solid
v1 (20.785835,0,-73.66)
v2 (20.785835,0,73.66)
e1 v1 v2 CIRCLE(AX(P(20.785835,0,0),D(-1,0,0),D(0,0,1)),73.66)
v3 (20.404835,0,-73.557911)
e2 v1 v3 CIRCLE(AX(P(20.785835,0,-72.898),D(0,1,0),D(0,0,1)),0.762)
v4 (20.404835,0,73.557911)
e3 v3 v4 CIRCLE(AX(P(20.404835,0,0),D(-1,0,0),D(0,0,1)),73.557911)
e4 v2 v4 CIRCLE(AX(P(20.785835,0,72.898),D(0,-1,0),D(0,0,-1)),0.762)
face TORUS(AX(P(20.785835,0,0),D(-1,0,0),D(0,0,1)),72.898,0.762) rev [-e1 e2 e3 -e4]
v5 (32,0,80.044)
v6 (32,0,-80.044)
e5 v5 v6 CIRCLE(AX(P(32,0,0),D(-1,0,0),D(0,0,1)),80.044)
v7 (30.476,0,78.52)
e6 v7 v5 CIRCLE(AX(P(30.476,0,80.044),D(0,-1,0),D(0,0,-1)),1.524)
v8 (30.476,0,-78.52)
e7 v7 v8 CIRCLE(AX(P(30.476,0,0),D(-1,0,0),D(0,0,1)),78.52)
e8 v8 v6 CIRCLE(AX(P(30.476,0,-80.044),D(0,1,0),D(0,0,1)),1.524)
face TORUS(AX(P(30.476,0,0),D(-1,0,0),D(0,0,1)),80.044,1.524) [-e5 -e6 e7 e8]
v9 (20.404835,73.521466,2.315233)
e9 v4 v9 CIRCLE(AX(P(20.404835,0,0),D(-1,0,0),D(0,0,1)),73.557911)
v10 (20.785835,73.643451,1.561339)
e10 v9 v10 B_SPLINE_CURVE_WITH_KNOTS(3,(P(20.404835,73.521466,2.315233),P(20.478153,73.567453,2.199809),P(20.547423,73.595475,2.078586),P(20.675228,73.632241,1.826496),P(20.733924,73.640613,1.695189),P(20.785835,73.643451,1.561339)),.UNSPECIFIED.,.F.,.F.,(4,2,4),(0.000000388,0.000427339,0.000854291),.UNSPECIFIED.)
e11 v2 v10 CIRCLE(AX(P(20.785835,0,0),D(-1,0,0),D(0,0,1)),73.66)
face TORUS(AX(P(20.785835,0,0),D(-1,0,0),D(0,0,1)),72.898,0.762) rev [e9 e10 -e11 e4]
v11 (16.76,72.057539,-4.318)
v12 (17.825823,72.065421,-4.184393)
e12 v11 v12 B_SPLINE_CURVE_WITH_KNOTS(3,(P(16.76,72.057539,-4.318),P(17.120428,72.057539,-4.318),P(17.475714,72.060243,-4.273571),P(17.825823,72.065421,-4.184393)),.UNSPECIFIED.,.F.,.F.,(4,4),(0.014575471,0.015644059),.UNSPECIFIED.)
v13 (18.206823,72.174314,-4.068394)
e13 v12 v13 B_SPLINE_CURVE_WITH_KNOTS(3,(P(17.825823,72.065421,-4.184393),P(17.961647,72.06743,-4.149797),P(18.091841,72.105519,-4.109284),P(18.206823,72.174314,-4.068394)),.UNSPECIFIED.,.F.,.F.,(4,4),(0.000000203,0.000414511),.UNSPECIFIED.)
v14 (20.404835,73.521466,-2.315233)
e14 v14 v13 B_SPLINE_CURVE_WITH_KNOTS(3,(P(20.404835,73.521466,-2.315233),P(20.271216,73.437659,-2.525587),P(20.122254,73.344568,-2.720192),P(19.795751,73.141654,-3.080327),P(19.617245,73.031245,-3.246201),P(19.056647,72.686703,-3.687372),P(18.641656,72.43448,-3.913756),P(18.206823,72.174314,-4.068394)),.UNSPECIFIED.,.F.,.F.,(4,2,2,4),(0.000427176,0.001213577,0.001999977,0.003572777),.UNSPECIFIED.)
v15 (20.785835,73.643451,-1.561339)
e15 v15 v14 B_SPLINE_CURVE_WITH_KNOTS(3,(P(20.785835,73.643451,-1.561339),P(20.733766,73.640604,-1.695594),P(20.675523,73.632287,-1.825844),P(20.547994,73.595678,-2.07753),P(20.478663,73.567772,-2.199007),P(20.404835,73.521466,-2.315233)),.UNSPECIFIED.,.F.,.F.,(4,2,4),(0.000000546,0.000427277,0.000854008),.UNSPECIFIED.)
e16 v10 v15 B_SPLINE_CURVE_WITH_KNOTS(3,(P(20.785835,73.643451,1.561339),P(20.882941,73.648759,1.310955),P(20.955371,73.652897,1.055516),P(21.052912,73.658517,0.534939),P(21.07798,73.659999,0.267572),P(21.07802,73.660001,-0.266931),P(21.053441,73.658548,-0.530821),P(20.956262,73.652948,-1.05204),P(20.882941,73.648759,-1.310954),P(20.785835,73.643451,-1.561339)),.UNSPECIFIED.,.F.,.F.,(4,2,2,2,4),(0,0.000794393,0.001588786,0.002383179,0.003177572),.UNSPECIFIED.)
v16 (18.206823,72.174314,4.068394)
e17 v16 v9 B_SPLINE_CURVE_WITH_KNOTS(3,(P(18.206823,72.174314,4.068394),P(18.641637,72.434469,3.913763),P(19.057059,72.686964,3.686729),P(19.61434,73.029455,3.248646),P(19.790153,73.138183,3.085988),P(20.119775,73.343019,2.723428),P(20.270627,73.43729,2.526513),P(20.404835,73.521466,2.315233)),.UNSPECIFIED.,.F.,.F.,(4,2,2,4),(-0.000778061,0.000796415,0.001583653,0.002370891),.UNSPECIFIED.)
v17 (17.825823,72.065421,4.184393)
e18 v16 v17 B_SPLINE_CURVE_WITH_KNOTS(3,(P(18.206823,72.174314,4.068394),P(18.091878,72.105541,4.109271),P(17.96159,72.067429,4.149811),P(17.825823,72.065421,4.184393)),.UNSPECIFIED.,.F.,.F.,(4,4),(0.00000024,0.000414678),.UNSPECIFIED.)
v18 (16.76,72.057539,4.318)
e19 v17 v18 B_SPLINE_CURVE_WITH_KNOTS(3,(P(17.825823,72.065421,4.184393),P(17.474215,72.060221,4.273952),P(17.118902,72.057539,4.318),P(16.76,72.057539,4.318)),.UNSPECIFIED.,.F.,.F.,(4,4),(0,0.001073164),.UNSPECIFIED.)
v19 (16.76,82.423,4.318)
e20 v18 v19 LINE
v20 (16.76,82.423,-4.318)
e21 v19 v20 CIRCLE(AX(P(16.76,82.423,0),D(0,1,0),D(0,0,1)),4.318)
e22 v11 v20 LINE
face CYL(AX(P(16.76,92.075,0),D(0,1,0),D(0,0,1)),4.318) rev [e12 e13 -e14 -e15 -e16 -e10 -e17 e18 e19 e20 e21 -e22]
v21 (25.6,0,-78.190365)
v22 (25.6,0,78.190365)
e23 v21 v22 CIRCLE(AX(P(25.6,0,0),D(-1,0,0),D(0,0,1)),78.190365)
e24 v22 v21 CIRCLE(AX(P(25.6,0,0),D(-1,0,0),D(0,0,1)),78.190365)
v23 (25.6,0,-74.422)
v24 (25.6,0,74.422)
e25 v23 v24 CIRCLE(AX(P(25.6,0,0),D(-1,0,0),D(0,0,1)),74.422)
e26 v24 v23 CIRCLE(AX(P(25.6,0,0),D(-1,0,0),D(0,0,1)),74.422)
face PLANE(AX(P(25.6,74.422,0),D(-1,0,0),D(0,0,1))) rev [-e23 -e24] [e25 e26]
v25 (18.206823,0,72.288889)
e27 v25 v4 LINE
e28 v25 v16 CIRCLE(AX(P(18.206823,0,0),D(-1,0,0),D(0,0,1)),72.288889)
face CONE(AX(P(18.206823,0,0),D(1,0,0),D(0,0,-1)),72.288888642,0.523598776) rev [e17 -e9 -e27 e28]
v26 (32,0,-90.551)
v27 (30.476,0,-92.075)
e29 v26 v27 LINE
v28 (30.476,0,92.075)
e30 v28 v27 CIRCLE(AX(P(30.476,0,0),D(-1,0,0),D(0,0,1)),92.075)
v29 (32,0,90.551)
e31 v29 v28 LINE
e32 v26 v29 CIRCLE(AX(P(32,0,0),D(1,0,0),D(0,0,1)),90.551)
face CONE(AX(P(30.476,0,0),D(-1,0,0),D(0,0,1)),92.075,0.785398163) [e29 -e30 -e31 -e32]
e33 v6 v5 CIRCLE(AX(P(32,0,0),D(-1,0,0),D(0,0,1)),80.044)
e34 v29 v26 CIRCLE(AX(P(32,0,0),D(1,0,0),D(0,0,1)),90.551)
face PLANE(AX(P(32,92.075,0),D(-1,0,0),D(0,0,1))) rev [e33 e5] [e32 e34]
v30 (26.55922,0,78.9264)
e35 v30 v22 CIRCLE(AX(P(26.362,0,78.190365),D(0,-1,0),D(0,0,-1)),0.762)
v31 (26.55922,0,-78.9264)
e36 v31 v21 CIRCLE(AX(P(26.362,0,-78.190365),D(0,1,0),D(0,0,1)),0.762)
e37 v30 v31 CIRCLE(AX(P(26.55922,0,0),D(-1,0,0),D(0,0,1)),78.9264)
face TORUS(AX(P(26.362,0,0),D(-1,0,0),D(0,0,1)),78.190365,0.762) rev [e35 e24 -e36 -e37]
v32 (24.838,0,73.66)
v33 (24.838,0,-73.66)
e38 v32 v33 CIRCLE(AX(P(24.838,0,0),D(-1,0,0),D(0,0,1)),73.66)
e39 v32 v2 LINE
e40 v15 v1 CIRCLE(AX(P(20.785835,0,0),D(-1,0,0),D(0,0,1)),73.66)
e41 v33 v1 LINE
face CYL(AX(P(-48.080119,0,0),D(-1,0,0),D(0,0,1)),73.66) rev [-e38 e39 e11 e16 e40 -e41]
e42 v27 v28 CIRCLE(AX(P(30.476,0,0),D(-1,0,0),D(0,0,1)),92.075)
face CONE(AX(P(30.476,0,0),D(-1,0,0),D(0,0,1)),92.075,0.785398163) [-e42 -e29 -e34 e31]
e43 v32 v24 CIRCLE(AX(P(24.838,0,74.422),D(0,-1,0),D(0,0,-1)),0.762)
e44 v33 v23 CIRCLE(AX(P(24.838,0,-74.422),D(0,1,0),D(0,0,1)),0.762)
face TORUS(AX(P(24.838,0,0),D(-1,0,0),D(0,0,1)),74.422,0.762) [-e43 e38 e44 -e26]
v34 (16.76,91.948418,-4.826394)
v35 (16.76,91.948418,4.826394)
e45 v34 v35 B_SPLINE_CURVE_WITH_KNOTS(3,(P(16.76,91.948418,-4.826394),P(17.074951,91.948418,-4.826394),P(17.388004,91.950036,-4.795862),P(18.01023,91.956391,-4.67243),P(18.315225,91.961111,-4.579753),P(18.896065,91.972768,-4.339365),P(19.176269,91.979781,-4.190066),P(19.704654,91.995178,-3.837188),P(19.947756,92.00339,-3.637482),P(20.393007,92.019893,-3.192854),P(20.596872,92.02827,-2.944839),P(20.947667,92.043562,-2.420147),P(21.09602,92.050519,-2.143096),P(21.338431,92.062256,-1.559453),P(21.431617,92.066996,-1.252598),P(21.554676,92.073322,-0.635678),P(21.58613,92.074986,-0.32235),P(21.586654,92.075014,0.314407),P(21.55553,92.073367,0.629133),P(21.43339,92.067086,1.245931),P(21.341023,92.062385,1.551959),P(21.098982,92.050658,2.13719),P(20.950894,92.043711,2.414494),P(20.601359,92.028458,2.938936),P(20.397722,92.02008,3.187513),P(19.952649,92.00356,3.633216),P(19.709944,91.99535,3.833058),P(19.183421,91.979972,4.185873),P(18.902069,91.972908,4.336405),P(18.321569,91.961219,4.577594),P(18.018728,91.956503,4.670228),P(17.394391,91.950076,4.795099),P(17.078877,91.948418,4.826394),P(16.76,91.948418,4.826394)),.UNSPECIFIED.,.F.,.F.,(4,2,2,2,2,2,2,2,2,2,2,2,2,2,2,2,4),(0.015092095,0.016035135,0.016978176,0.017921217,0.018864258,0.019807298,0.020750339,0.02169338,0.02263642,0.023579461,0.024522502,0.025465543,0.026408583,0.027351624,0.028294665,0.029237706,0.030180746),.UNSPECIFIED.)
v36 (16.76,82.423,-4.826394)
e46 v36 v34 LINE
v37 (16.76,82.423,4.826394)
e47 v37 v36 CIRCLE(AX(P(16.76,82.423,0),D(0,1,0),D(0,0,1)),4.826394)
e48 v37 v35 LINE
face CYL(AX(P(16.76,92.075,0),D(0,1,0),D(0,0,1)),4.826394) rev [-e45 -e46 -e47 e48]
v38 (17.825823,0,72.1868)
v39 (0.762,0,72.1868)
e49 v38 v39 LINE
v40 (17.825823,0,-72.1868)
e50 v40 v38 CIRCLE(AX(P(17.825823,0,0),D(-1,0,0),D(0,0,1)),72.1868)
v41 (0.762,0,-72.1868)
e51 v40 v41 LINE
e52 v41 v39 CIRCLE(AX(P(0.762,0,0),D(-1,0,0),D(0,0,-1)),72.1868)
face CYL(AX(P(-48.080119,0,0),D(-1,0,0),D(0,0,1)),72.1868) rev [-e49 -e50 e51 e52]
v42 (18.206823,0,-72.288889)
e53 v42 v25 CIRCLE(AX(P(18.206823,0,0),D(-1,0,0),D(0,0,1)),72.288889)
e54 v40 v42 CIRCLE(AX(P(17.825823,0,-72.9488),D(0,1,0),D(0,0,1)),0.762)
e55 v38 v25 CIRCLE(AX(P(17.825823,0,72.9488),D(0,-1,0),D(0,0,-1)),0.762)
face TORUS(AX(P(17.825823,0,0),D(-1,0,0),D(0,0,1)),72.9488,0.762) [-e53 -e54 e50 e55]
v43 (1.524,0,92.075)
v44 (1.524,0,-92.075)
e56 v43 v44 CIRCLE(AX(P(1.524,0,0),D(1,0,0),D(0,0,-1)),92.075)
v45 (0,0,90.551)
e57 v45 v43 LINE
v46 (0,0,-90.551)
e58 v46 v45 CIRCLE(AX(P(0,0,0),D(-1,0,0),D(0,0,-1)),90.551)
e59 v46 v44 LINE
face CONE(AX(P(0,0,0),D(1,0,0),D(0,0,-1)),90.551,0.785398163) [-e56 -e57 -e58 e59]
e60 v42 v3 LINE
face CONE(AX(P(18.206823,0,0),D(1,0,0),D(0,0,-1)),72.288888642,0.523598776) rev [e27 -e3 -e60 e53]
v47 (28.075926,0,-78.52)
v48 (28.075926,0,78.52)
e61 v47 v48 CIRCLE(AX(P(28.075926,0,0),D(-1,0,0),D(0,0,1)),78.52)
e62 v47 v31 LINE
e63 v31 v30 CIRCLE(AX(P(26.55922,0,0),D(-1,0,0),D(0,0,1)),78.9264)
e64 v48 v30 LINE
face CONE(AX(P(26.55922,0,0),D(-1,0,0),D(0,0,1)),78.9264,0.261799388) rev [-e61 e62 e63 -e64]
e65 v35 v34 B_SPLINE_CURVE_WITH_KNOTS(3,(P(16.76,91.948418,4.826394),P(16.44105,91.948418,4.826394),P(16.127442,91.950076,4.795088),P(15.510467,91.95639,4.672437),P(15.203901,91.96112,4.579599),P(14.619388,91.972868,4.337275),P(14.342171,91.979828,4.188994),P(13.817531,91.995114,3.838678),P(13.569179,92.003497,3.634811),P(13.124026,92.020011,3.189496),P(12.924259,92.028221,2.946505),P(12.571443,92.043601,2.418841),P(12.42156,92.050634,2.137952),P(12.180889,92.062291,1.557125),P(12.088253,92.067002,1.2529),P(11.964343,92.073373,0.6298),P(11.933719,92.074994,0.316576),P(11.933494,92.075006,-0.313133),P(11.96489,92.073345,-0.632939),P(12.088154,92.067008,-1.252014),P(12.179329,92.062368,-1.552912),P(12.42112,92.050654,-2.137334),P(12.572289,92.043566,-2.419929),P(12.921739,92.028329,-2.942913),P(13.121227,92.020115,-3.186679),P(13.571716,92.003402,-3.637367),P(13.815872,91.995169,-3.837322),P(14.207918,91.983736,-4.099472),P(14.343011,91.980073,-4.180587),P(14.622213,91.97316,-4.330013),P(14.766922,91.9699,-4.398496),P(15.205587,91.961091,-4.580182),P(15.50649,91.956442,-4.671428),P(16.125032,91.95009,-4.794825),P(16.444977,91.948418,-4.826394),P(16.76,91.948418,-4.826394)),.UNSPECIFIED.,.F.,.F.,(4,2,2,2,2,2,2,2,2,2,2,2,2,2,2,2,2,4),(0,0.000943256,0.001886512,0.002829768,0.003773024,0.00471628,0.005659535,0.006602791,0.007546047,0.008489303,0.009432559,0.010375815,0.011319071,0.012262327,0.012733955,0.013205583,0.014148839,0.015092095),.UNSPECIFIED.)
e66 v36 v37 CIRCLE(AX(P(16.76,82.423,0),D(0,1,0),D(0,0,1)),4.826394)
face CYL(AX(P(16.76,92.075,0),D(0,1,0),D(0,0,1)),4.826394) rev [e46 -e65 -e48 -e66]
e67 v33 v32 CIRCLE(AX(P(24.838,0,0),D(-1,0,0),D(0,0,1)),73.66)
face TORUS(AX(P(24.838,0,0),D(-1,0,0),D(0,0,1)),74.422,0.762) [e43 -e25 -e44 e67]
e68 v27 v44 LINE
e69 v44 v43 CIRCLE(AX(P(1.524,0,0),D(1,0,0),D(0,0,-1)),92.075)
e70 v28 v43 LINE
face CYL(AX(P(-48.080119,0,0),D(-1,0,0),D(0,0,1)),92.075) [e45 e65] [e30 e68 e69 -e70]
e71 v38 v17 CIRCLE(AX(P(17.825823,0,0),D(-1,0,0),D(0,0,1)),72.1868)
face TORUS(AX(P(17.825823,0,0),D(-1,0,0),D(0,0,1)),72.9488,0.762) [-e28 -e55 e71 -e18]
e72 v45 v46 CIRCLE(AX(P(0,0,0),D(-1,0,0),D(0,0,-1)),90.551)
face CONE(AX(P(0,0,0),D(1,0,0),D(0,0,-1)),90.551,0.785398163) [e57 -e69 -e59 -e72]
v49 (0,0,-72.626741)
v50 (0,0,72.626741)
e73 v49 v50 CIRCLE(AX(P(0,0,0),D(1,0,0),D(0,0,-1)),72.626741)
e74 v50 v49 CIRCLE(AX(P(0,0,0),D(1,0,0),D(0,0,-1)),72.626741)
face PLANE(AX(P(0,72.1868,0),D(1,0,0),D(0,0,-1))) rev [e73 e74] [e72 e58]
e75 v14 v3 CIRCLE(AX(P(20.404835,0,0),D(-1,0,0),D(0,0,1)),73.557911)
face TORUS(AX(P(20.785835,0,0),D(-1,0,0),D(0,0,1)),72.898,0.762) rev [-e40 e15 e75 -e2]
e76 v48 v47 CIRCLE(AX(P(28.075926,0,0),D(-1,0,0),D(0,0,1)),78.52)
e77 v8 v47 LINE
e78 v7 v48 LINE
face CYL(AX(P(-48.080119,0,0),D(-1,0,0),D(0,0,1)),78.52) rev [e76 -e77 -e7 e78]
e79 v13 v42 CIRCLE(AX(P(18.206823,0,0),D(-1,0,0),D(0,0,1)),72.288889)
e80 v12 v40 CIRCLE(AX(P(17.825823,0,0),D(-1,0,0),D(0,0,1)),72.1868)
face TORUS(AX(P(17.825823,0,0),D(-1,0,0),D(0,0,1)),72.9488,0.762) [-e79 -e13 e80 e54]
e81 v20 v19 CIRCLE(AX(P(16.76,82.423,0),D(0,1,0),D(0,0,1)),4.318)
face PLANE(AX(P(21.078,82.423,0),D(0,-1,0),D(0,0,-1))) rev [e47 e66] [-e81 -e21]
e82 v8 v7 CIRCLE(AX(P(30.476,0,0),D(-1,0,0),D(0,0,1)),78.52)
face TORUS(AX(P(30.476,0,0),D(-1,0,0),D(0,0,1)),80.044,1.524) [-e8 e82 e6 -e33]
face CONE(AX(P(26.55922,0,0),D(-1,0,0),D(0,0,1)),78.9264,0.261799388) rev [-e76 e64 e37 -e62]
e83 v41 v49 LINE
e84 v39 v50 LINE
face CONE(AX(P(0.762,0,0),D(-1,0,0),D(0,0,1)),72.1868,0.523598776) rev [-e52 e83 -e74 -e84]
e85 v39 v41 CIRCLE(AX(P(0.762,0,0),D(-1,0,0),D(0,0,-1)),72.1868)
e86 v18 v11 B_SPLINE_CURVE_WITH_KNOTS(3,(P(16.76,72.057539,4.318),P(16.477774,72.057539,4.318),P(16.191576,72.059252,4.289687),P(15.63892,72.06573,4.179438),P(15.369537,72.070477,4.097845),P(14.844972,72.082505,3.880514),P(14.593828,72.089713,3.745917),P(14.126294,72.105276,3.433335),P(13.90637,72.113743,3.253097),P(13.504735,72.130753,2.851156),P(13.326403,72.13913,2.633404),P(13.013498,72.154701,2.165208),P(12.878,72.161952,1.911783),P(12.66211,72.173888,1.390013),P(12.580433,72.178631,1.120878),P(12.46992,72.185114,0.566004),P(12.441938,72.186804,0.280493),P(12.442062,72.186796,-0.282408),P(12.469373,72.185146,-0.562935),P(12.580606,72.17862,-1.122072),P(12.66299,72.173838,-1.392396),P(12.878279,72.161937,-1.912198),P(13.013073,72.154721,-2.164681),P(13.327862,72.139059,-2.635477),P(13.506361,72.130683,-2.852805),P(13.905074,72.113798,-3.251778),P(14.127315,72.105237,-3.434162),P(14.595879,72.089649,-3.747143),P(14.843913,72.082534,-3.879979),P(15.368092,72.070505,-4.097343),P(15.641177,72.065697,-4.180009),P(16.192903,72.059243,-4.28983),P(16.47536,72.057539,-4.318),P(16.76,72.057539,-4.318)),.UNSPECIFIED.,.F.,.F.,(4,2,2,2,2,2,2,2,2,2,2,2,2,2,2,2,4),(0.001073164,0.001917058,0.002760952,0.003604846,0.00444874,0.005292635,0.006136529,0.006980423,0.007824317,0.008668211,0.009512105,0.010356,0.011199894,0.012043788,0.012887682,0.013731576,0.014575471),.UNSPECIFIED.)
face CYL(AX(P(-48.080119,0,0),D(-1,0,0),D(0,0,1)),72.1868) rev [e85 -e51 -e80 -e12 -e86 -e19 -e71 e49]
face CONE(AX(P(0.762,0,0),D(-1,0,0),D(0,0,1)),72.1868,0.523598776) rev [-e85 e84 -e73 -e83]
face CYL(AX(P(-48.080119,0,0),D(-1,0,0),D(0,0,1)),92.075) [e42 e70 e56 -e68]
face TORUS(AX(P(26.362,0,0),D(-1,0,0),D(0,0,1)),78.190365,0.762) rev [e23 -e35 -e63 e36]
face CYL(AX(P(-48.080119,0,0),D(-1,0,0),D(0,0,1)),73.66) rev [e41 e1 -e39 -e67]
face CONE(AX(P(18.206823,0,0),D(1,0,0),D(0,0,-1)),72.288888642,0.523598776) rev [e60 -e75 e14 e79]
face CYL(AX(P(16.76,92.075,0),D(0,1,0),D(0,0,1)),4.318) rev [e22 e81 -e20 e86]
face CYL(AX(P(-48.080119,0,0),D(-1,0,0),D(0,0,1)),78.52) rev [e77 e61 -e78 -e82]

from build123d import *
from build123d.topology import SkipClean

# Parameters (mm, degrees)
CHAMFER2_SIZE                      = 0.762
CHAMFER2_SIZE2                     = 0.439940905
CHAMFER3_SIZE                      = 1.524
F_1_8_NPT_TAPPED_HOLE1_D           = 8.636
F_1_8_NPT_TAPPED_HOLE1_DEPTH       = 19.431
F_1_8_NPT_TAPPED_HOLE1_CBORE_D     = 9.6527874
F_1_8_NPT_TAPPED_HOLE1_CBORE_DEPTH = 9.652
F_1_8_NPT_TAPPED_HOLE1_TIP         = 2.594516153
SKETCH4_R                          = 4.318
CUT_EXTRUDE1_DEPTH                 = 82.423


with BuildPart() as part:
    # Sketch1 → Revolve1 (revolve)
    with BuildSketch(Plane.XY, mode=Mode.PRIVATE) as revolve1_sk:
        with BuildLine():
            Line((0, 92.075), (32, 92.075))
            Line((32, 92.075), (32, 80.044))
            ThreePointArc((32, 80.044), (31.553630735, 78.966369265), (30.476, 78.52))
            Line((30.476, 78.52), (28.075925561, 78.52))
            Line((28.075925561, 78.52), (26.559220112, 78.9264))
            ThreePointArc((26.559220112, 78.9264), (25.898123791, 78.794899766), (25.6, 78.19036452))
            Line((25.6, 78.19036452), (25.6, 74.422))
            ThreePointArc((25.6, 74.422), (25.376815367, 73.883184633), (24.838, 73.66))
            Line((24.838, 73.66), (20.785834534, 73.66))
            ThreePointArc((20.785834534, 73.66), (20.588614422, 73.63403548), (20.404834534, 73.557911358))
            Line((20.404834534, 73.557911358), (18.206822715, 72.288888642))
            ThreePointArc((18.206822715, 72.288888642), (18.023042828, 72.21276452), (17.825822715, 72.1868))
            Line((17.825822715, 72.1868), (0, 72.1868))
            Line((0, 72.1868), (0, 92.075))
        make_face()
    revolve(revolve1_sk.sketch.rotate(Axis((-48.080119454, 0, 0), (1, 0, 0)), 90), axis=Axis((-48.080119454, 0, 0), (1, 0, 0)))

    # Chamfer2
    chamfer2_edges = [part.edges().sort_by_distance(p)[0] for p in [
        (0, 0, -72.1868),
    ]]
    chamfer2_side = [part.faces().sort_by_distance(p)[0] for p in [
        (8.912911358, 0, -72.1868),
    ]]
    chamfer(chamfer2_edges, length=CHAMFER2_SIZE, length2=CHAMFER2_SIZE2, reference=chamfer2_side[0])

    # Chamfer3
    chamfer3_edges = [part.edges().sort_by_distance(p)[0] for p in [
        (32, 0, -92.075),
        (0, 0, -92.075),
    ]]
    chamfer(chamfer3_edges, length=CHAMFER3_SIZE)

    # 1/8 NPT Tapped Hole1
    with Locations(Plane(origin=(16.76, 92.075, 0), x_dir=(0, 0, 1), z_dir=(0, 1, 0))):
        with Locations((0, 0)):
            CounterBoreHole(F_1_8_NPT_TAPPED_HOLE1_D / 2, F_1_8_NPT_TAPPED_HOLE1_CBORE_D / 2, F_1_8_NPT_TAPPED_HOLE1_CBORE_DEPTH, depth=F_1_8_NPT_TAPPED_HOLE1_DEPTH)
            with Locations((0, 0, -(F_1_8_NPT_TAPPED_HOLE1_DEPTH + F_1_8_NPT_TAPPED_HOLE1_TIP / 2))):  # 118° drill point
                Cone(0, F_1_8_NPT_TAPPED_HOLE1_D / 2, F_1_8_NPT_TAPPED_HOLE1_TIP, mode=Mode.SUBTRACT)

    # Sketch4 → Cut-Extrude1 (cut)
    with SkipClean():  # the faces are left unmerged after this step: merging them gives an invalid solid
        with BuildSketch(Plane(origin=(0, 0, 0), x_dir=(1, 0, 0), z_dir=(0, 1, 0))):
            with Locations(Location((16.76, 0, 0), (0, 0, 270))):
                Circle(SKETCH4_R)
        extrude(amount=CUT_EXTRUDE1_DEPTH, mode=Mode.SUBTRACT)


solid = part.part
